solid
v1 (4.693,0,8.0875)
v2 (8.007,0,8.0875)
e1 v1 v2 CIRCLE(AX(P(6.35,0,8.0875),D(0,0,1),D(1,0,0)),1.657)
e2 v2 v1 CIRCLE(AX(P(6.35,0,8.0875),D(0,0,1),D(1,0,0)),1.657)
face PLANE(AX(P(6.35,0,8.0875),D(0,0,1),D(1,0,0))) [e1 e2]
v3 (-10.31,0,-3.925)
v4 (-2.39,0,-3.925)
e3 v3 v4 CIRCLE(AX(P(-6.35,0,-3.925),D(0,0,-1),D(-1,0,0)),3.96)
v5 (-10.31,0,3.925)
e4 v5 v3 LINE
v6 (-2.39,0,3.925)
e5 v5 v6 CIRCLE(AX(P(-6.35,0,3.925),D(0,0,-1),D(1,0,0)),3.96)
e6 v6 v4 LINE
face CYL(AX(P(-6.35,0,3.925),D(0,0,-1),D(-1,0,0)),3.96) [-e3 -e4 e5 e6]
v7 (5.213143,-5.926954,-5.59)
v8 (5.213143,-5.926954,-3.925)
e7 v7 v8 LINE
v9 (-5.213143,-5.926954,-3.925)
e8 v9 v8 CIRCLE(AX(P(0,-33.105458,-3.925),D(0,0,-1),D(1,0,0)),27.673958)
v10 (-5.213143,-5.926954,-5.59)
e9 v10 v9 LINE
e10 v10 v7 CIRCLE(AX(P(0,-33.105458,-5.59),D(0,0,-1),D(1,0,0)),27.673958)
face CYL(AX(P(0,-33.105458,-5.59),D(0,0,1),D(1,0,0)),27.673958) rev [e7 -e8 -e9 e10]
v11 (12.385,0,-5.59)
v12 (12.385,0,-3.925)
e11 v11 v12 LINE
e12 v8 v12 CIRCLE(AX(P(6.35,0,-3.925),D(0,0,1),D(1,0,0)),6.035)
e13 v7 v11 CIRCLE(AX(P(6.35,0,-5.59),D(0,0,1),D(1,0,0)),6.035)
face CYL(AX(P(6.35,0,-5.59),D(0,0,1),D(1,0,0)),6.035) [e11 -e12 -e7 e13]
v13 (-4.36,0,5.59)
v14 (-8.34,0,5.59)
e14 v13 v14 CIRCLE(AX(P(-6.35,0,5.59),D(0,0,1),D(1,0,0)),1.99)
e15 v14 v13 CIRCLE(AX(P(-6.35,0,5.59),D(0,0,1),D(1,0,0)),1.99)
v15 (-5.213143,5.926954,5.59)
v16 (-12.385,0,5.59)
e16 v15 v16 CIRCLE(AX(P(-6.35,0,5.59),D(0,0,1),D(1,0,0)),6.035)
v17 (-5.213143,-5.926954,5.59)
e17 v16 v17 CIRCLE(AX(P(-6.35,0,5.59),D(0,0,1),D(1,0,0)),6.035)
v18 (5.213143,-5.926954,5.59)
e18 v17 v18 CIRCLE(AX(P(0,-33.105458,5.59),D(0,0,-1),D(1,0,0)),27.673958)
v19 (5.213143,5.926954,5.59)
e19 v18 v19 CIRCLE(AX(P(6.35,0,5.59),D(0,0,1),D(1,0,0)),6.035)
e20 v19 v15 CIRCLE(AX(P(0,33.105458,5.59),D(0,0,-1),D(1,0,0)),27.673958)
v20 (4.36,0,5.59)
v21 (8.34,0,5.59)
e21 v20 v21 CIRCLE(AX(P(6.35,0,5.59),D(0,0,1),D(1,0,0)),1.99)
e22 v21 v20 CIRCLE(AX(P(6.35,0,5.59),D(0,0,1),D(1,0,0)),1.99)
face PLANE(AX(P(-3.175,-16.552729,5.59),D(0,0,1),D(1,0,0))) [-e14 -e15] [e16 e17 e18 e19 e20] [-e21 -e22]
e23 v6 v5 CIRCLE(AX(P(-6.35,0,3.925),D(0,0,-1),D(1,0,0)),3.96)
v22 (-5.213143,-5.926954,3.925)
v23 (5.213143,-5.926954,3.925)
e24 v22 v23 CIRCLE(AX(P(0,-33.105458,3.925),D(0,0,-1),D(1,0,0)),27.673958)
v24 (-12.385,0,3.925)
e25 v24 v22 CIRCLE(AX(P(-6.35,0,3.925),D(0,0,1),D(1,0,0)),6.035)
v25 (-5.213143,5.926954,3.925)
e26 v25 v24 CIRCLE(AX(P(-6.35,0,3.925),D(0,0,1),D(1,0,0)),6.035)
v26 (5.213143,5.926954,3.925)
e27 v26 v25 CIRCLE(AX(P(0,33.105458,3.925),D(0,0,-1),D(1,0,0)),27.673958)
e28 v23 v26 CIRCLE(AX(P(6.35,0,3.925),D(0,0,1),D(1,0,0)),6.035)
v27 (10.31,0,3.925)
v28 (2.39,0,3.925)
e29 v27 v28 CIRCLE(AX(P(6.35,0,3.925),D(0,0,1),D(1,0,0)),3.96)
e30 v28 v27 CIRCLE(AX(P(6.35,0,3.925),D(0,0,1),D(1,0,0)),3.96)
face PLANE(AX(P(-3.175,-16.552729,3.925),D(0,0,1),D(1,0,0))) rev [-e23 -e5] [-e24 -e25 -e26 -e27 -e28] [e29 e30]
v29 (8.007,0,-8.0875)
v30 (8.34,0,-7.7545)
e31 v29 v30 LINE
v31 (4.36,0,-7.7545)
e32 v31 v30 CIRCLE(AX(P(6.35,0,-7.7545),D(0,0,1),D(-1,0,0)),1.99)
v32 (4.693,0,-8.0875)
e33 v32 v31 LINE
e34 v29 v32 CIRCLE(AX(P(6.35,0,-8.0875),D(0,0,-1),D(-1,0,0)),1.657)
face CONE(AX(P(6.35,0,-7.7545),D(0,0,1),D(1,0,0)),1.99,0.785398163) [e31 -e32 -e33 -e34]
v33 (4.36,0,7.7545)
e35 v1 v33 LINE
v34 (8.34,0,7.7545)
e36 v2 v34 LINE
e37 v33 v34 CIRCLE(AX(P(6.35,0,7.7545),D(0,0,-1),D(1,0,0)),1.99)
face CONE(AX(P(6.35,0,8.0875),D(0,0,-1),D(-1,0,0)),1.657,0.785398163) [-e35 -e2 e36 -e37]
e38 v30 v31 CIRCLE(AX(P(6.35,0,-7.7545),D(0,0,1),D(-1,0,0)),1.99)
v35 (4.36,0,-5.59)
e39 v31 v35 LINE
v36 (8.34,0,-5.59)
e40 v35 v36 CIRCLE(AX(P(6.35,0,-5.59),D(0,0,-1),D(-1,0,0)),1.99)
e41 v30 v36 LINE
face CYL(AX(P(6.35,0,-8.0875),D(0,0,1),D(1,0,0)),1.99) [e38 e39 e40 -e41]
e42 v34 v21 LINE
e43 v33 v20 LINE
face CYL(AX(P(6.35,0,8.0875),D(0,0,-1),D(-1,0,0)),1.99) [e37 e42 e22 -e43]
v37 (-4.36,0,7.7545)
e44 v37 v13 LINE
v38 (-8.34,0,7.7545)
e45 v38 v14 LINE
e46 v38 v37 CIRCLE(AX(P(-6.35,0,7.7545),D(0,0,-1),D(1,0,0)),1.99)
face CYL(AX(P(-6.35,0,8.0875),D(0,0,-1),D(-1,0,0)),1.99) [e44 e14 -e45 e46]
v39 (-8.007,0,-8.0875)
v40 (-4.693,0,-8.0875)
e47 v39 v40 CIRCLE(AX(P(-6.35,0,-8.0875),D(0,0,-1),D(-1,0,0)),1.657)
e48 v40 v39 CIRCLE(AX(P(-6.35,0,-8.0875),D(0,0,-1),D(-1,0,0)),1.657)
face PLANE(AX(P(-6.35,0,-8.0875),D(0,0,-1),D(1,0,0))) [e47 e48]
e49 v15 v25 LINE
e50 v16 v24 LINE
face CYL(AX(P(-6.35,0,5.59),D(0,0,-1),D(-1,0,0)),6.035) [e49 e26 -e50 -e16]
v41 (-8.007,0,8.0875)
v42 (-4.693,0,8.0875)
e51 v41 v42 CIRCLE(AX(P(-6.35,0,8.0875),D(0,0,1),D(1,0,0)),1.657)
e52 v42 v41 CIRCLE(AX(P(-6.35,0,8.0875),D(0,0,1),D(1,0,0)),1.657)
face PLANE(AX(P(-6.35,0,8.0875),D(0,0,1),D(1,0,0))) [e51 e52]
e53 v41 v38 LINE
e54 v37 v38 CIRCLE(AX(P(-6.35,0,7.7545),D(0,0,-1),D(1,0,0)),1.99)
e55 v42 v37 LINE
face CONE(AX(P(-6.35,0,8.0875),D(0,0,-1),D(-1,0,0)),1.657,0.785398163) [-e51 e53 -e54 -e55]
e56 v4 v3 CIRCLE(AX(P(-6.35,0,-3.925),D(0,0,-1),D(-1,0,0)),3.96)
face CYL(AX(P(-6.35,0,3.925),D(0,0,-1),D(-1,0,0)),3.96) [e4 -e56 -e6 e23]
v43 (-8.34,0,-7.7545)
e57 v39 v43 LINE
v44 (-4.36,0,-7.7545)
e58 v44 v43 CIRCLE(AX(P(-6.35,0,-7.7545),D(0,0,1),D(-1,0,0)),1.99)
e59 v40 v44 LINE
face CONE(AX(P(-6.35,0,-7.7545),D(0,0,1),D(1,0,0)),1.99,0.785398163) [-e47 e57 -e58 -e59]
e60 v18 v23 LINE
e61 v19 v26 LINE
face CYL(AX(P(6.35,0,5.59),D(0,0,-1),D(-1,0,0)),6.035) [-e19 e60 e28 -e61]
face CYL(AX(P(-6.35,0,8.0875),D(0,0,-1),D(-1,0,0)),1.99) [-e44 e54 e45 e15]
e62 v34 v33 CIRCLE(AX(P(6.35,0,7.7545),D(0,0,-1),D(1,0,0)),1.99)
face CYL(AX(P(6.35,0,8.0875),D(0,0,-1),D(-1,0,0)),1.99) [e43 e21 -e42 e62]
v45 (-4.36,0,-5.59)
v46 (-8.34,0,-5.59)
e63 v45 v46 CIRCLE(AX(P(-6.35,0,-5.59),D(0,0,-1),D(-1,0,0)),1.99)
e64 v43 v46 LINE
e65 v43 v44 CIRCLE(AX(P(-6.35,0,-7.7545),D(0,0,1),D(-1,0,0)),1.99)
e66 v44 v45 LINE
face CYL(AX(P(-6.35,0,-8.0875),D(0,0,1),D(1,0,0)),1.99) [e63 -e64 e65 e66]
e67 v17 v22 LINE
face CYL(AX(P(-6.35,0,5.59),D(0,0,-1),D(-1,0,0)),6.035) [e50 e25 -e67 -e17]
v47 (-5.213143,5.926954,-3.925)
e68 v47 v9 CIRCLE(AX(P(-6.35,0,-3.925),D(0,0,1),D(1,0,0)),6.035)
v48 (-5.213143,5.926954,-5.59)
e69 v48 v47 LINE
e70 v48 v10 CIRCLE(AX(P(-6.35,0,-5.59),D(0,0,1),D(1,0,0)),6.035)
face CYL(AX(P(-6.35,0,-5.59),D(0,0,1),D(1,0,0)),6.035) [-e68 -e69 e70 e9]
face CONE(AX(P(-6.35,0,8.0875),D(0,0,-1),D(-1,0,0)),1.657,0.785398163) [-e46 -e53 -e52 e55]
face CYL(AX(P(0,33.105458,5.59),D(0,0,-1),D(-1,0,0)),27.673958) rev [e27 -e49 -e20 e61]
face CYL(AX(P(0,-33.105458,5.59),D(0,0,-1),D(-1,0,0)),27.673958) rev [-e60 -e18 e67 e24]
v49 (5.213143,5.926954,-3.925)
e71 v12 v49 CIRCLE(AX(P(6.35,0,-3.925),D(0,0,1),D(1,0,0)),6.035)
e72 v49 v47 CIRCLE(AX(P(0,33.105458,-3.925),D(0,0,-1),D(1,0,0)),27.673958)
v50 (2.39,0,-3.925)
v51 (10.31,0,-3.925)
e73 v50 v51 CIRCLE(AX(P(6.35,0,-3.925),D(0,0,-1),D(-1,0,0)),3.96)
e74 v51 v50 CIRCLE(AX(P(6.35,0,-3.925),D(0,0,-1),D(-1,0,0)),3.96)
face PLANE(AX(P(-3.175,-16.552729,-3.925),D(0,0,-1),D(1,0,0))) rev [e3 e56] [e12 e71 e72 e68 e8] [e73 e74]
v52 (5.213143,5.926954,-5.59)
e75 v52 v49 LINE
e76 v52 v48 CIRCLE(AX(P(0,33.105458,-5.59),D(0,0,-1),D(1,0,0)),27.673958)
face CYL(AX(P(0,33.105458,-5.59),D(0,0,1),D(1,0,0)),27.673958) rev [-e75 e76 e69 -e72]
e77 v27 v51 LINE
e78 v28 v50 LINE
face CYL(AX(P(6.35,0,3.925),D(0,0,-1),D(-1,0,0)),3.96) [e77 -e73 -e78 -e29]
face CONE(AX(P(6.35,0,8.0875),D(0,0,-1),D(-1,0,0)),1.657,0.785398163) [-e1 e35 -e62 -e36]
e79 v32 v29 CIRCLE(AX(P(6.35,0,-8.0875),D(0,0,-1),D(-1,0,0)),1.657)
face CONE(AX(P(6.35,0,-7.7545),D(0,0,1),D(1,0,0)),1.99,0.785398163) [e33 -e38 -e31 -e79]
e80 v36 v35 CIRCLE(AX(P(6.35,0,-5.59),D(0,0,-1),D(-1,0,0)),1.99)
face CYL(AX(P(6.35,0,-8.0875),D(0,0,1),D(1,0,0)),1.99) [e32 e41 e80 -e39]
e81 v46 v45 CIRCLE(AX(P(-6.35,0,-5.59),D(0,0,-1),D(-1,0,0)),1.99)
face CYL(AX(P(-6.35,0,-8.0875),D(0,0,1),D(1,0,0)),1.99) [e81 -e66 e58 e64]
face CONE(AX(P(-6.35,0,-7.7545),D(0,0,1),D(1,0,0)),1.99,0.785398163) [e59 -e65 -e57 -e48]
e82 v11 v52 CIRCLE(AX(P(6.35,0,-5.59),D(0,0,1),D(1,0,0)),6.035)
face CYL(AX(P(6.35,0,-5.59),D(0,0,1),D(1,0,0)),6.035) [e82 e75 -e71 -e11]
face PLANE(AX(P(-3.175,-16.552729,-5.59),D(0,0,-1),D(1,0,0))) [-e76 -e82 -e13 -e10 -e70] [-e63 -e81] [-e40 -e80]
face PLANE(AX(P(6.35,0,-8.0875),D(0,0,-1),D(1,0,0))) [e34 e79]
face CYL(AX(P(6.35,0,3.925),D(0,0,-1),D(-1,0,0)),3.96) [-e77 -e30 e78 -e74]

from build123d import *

# Parameters (mm, degrees)
SKETCH_2_R                 = 3.96
EXTRUDE_1_DEPTH            = 3.925
EXTRUDE_1_2_DEPTH          = 3.925
EXTRUDE_2_DEPTH            = 1.665
SKETCH_4_R                 = 1.99
EXTRUDE_3_DEPTH            = 2.4975
CHAMFER_1_SIZE             = 0.333
CHAMFER_1_OF_MIRROR_1_SIZE = 0.333


with BuildPart() as part:
    # 草图2 → 拉伸1 (new, symmetric)
    with BuildSketch(Plane.XY):
        with Locations((6.35, 0)):
            Circle(SKETCH_2_R)
    extrude(amount=EXTRUDE_1_DEPTH, both=True)



with BuildPart() as body_2:
    # 草图2 → Extrude 1 2 (new, symmetric)
    with BuildSketch(Plane.XY):
        with Locations((-6.35, 0)):
            Circle(SKETCH_2_R)
    extrude(amount=EXTRUDE_1_2_DEPTH, both=True)


with BuildPart() as part_1:
    add(part.part)

    add(body_2.part)  # 拉伸2 merges body 2
    # 草图3 → 拉伸2 (add)
    with BuildSketch(Plane.XY.offset(3.925)):
        with BuildLine():
            ThreePointArc((-5.213143439, 5.926953869), (-12.385, 0), (-5.213143439, -5.926953869))
            ThreePointArc((-5.213143439, -5.926953869), (0, -5.4315), (5.213143439, -5.926953869))
            ThreePointArc((5.213143439, -5.926953869), (12.385, 0), (5.213143439, 5.926953869))
            ThreePointArc((5.213143439, 5.926953869), (0, 5.4315), (-5.213143439, 5.926953869))
        make_face()
    extrude_2 = extrude(amount=EXTRUDE_2_DEPTH)

    # 草图4 → 拉伸3 (add)
    with BuildSketch(Plane.XY.offset(5.59)):
        with Locations((6.35, 0)):
            Circle(SKETCH_4_R)
        with Locations((-6.35, 0)):
            Circle(SKETCH_4_R)
    extrude_3 = extrude(amount=EXTRUDE_3_DEPTH)

    # 倒角1
    chamfer_1_edges = [part_1.edges().sort_by_distance(p)[0] for p in [
        (4.36, 0, 8.0875),
        (-8.34, 0, 8.0875),
    ]]
    chamfer(chamfer_1_edges, length=CHAMFER_1_SIZE)

    # 镜向1: 拉伸2, 拉伸3 across plane
    add(extrude_2.mirror(Plane.XY))
    add(extrude_3.mirror(Plane.XY))

    # 倒角1 of 镜向1
    chamfer_1_of_mirror_1_edges = [part_1.edges().sort_by_distance(p)[0] for p in [
        (4.36, 0, -8.0875),
        (-8.34, 0, -8.0875),
    ]]
    chamfer(chamfer_1_of_mirror_1_edges, length=CHAMFER_1_OF_MIRROR_1_SIZE)


solid = part_1.part
